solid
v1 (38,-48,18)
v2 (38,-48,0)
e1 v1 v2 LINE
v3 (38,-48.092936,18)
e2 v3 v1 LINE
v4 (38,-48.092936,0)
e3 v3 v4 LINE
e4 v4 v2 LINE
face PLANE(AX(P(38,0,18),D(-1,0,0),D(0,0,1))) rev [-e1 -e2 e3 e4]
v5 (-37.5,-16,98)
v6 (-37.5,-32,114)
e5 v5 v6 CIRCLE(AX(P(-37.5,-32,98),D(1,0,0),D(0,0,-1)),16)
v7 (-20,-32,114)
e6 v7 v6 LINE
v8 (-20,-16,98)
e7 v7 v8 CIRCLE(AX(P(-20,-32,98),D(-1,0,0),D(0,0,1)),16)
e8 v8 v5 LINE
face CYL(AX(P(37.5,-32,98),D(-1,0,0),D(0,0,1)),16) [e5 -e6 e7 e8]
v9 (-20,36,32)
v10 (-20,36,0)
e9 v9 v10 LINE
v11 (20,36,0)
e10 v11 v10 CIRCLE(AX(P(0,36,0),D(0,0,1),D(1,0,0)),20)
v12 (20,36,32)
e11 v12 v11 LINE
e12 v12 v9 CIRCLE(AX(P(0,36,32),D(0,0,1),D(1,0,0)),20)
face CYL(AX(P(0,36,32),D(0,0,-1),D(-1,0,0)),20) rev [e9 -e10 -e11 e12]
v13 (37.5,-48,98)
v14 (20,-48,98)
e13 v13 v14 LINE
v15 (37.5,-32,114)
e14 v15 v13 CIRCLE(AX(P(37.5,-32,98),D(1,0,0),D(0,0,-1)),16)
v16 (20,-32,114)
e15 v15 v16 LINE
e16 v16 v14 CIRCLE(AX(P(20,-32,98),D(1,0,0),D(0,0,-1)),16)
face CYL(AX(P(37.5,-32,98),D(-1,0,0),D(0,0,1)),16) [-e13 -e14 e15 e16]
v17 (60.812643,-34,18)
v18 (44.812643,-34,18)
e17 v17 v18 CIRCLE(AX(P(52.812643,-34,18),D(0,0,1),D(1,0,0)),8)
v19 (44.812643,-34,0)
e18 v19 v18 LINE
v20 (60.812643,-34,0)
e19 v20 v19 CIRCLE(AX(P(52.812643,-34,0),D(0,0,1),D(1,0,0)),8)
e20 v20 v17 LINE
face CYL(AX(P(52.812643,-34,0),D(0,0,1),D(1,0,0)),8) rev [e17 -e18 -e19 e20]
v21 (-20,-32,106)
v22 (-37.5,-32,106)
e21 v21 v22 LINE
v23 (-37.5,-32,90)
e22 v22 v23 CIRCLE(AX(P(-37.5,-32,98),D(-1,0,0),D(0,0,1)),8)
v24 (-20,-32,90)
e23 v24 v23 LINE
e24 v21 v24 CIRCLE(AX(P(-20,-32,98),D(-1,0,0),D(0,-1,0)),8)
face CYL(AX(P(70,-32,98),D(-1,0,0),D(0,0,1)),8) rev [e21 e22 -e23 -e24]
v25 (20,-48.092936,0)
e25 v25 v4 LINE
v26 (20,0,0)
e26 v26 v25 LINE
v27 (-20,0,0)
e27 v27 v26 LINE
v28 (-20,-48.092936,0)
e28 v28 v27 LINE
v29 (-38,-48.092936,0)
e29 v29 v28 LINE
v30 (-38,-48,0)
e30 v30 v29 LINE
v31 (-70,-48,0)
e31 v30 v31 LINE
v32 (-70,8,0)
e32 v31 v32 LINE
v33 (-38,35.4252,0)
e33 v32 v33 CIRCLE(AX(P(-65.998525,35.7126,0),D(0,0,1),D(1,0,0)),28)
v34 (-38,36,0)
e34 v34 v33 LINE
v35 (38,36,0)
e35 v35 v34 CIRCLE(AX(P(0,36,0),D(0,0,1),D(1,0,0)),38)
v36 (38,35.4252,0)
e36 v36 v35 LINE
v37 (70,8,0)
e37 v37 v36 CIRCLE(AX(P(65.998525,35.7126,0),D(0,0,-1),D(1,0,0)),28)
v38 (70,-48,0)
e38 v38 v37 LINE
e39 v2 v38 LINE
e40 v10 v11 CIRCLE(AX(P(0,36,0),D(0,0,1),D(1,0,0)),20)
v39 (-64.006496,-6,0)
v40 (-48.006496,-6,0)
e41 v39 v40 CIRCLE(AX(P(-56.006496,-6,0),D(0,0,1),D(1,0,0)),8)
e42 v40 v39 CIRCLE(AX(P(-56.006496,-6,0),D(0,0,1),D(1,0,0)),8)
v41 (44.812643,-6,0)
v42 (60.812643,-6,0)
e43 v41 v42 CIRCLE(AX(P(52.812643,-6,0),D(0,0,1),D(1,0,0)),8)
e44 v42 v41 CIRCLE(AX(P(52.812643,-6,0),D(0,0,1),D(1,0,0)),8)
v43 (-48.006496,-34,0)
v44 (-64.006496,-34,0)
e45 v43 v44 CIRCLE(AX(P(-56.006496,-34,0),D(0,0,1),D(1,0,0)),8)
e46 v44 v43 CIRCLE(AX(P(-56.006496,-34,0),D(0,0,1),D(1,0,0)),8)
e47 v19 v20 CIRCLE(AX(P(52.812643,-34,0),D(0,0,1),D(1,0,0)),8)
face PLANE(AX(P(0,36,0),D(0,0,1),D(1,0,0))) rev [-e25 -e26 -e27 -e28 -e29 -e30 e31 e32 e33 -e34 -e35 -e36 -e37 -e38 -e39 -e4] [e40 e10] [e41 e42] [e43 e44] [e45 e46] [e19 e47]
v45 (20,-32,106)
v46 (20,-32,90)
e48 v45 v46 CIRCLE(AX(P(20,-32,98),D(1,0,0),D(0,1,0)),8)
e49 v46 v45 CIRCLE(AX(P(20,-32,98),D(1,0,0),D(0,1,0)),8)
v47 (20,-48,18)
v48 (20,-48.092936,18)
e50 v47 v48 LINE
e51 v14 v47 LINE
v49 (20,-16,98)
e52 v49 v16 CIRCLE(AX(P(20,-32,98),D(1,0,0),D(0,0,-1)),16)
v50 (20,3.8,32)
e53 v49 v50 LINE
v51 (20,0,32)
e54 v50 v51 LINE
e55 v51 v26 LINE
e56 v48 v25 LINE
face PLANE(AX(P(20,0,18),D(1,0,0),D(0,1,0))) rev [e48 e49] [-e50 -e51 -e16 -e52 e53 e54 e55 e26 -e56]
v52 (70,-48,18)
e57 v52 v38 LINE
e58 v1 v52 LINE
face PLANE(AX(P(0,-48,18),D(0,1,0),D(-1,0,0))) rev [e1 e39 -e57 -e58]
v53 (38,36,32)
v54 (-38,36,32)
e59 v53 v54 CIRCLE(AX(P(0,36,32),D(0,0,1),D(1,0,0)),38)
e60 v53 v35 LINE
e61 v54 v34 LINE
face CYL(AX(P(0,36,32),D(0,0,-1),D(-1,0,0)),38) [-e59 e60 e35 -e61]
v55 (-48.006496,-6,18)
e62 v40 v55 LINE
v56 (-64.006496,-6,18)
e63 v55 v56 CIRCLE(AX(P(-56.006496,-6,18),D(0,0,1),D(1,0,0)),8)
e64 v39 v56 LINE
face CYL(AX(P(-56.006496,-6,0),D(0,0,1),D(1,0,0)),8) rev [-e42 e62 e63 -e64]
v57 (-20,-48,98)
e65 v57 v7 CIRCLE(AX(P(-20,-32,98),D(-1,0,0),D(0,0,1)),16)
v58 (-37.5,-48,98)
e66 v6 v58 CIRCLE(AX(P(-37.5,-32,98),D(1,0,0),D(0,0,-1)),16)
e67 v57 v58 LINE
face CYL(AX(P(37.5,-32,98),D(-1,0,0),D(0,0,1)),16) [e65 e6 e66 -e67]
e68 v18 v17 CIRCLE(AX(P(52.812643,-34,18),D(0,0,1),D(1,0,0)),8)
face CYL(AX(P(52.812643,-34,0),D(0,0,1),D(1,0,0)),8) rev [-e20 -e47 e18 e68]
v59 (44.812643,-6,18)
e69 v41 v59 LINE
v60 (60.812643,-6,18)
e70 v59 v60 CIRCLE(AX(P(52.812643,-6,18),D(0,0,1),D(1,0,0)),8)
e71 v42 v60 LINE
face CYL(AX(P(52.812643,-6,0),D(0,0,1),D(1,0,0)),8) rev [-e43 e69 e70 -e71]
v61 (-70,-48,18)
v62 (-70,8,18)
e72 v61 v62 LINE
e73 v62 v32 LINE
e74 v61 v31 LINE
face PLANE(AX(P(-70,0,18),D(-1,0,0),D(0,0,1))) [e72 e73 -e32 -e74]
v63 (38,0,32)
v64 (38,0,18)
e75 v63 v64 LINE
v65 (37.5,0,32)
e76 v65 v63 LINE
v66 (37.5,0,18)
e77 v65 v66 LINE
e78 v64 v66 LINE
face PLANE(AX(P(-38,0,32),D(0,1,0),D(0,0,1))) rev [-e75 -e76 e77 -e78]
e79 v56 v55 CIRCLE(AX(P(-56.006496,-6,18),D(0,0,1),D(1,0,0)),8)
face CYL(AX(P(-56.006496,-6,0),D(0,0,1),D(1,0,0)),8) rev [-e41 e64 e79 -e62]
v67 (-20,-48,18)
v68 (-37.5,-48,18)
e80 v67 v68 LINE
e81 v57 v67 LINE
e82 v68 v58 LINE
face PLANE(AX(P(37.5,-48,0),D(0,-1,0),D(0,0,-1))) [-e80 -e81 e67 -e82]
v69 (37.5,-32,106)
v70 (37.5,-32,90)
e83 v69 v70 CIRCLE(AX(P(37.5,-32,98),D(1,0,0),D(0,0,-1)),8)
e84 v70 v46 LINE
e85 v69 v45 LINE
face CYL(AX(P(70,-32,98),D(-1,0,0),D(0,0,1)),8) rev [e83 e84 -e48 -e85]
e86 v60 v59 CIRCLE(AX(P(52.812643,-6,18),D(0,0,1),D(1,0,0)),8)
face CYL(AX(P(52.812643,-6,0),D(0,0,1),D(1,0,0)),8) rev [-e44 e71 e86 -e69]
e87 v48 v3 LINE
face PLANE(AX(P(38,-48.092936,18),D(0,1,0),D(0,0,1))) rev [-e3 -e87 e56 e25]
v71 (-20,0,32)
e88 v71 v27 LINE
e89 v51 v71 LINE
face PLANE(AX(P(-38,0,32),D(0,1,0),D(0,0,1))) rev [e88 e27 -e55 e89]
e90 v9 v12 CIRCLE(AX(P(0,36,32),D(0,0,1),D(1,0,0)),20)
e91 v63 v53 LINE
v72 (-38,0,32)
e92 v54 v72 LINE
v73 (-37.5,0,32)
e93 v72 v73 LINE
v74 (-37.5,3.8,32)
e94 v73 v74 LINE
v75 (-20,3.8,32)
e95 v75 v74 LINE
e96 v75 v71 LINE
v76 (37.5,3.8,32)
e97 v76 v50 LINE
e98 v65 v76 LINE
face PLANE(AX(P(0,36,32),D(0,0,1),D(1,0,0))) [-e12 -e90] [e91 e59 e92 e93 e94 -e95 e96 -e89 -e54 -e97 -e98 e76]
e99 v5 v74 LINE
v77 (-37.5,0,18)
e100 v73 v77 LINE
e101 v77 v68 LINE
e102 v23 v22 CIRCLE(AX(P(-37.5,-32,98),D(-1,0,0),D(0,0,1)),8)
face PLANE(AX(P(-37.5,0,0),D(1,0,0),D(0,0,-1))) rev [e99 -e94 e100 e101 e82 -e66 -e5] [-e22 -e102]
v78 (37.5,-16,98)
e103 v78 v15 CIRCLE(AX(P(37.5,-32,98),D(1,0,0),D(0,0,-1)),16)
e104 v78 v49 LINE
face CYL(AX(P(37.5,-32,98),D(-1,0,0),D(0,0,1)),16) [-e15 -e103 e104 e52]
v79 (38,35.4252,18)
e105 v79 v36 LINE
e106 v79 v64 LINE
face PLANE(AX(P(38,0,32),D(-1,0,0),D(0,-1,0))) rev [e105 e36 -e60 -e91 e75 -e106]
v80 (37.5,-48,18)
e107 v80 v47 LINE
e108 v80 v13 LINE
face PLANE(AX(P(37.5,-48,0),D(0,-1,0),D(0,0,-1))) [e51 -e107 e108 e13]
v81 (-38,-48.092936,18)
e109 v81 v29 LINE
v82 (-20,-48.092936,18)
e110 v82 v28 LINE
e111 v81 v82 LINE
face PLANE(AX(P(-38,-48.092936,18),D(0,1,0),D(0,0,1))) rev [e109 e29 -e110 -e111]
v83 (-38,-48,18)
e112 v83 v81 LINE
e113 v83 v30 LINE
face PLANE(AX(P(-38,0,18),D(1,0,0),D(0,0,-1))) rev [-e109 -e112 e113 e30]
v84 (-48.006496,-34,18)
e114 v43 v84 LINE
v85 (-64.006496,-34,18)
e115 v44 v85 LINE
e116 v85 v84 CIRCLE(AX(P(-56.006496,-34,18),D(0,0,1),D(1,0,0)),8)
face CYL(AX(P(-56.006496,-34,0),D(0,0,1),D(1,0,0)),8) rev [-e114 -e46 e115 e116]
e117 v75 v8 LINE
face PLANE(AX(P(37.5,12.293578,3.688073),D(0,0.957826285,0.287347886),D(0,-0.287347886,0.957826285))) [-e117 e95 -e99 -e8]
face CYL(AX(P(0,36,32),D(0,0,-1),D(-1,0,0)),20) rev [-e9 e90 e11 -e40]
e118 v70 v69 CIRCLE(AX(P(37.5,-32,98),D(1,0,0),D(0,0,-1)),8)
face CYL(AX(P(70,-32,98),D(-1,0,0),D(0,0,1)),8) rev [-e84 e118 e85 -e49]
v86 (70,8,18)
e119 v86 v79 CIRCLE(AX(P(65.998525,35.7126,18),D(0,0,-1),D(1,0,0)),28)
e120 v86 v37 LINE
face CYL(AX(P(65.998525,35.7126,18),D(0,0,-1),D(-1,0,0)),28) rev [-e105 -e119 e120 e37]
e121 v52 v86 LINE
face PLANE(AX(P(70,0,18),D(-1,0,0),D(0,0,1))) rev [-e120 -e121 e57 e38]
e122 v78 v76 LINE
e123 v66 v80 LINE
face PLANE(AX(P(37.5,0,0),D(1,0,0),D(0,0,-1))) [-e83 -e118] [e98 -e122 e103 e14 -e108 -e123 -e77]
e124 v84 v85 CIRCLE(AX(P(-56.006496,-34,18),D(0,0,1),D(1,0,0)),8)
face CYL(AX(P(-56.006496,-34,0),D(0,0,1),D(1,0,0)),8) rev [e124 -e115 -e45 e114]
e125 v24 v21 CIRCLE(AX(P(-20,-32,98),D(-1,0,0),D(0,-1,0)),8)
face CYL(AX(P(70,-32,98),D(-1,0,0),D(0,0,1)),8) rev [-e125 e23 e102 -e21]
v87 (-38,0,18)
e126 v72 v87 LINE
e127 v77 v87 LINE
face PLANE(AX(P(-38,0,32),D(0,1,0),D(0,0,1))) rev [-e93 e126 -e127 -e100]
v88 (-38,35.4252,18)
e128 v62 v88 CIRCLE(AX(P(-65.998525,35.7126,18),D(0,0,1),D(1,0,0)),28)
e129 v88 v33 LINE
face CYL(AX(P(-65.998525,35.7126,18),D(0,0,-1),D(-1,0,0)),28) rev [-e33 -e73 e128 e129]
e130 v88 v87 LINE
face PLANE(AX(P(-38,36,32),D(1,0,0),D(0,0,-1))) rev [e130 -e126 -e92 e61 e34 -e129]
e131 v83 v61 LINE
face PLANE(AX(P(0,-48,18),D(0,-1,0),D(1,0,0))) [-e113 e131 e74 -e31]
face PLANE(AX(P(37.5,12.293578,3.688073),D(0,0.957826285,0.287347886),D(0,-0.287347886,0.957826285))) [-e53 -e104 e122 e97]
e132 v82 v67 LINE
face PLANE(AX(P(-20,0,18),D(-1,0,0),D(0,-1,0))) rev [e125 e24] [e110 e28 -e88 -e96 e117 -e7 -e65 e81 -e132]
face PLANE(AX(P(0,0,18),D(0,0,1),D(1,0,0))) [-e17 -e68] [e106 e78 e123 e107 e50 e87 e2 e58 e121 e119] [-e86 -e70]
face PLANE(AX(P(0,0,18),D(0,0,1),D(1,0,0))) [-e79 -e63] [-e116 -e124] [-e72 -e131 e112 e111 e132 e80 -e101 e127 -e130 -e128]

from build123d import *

# Parameters (mm, degrees)
HUB_BODY_SKETCH_R             = 20
HUB_BODY_DEPTH                = 32
MOUNTING_PLATE_DEPTH          = 18
SIDE_WEB_SKETCH_W             = 18
SIDE_WEB_SKETCH_H             = 48.092935693
SIDE_WEB_DEPTH                = 18
FORK_ARMS_DEPTH               = 37.5
FORK_SLOT_SKETCH_W            = 40
FORK_SLOT_SKETCH_H            = 48
FORK_SLOT_DEPTH               = 140.971425655
HUB_RELIEF_CUT_DEPTH          = 153.87903715
FORK_PIN_HOLE_SKETCH_R        = 8
FORK_PIN_HOLE_16_DEPTH        = 174.286612293
PLATE_MOUNTING_HOLES_SKETCH_R = 8
PLATE_MOUNTING_HOLES_16_DEPTH = 140.971425655


with BuildPart() as part:
    # Hub Body Sketch → Hub Body (new body)
    with BuildSketch(Plane.XY):
        with BuildLine():
            Line((-38, 36), (-38, 0))
            Line((-38, 0), (38, 0))
            Line((38, 0), (38, 36))
            ThreePointArc((38, 36), (0, 74), (-38, 36))
        make_face()
        with Locations((0, 36)):
            Circle(HUB_BODY_SKETCH_R, mode=Mode.SUBTRACT)
    extrude(amount=HUB_BODY_DEPTH)

    # Mounting Plate Sketch → Mounting Plate (add)
    with BuildSketch(Plane.XY):
        with BuildLine():
            Line((-38, -48), (-38, 35.425199961))
            ThreePointArc((-38, 35.425199961), (-47.777657825, 14.452308355), (-70, 8))
            Line((-70, 8), (-70, -48))
            Line((-70, -48), (-38, -48))
        make_face()
        with BuildLine():
            ThreePointArc((70, 8), (47.777657825, 14.452308355), (38, 35.425199961))
            Line((38, 35.425199961), (38, -48))
            Line((38, -48), (70, -48))
            Line((70, -48), (70, 8))
        make_face()
    extrude(amount=MOUNTING_PLATE_DEPTH)

    # Side Web Sketch → Side Web (add)
    with BuildSketch(Plane.XY):
        with Locations((-29, -24.046467847)):
            Rectangle(SIDE_WEB_SKETCH_W, SIDE_WEB_SKETCH_H)
        with Locations((29, -24.046467847)):
            Rectangle(SIDE_WEB_SKETCH_W, SIDE_WEB_SKETCH_H)
    extrude(amount=SIDE_WEB_DEPTH)

    # Fork Arms Sketch → Fork Arms (add, symmetric)
    with BuildSketch(Plane(origin=(0, 0, 0), x_dir=(0, 0, -1), z_dir=(1, 0, 0))):
        with BuildLine():
            Line((-98, -48), (-18, -48))
            Line((-18, -48), (-18, 8))
            Line((-18, 8), (-98, -16))
            ThreePointArc((-98, -16), (-114, -32), (-98, -48))
        make_face()
    extrude(amount=FORK_ARMS_DEPTH, both=True)

    # Fork Slot Sketch → Fork Slot (cut, through all)
    with BuildSketch(Plane(origin=(0, 0, 18), x_dir=(-1, 0, 0), z_dir=(0, 0, -1))):
        with Locations((0, -24)):
            Rectangle(FORK_SLOT_SKETCH_W, FORK_SLOT_SKETCH_H)
    extrude(amount=-FORK_SLOT_DEPTH, mode=Mode.SUBTRACT)

    # Hub Relief Sketch → Hub Relief Cut (cut, through all)
    with BuildSketch(Plane(origin=(0, 0, 0), x_dir=(-1, 0, 0), z_dir=(0, -1, 0))):
        Polygon((-20, -44.666666667), (20, -44.666666667), (20, -32), (11.078422409, -32), (-20, -32), align=None)
    extrude(amount=-HUB_RELIEF_CUT_DEPTH, mode=Mode.SUBTRACT)

    # Fork Pin Hole Sketch → Fork Pin Hole Ø16 (cut, through all)
    with BuildSketch(Plane.ZY.offset(37.5)):
        with Locations((98, -32)):
            Circle(FORK_PIN_HOLE_SKETCH_R)
    extrude(amount=-FORK_PIN_HOLE_16_DEPTH, mode=Mode.SUBTRACT)

    # Plate Mounting Holes Sketch → Plate Mounting Holes Ø16 (cut, through all)
    with BuildSketch(Plane.XY.offset(18)):
        with Locations((-56.00649608, -6)):
            Circle(PLATE_MOUNTING_HOLES_SKETCH_R)
        with Locations((-56.00649608, -34)):
            Circle(PLATE_MOUNTING_HOLES_SKETCH_R)
        with Locations((52.812642943, -6)):
            Circle(PLATE_MOUNTING_HOLES_SKETCH_R)
        with Locations((52.812642943, -34)):
            Circle(PLATE_MOUNTING_HOLES_SKETCH_R)
    extrude(amount=-PLATE_MOUNTING_HOLES_16_DEPTH, mode=Mode.SUBTRACT)


solid = part.part
